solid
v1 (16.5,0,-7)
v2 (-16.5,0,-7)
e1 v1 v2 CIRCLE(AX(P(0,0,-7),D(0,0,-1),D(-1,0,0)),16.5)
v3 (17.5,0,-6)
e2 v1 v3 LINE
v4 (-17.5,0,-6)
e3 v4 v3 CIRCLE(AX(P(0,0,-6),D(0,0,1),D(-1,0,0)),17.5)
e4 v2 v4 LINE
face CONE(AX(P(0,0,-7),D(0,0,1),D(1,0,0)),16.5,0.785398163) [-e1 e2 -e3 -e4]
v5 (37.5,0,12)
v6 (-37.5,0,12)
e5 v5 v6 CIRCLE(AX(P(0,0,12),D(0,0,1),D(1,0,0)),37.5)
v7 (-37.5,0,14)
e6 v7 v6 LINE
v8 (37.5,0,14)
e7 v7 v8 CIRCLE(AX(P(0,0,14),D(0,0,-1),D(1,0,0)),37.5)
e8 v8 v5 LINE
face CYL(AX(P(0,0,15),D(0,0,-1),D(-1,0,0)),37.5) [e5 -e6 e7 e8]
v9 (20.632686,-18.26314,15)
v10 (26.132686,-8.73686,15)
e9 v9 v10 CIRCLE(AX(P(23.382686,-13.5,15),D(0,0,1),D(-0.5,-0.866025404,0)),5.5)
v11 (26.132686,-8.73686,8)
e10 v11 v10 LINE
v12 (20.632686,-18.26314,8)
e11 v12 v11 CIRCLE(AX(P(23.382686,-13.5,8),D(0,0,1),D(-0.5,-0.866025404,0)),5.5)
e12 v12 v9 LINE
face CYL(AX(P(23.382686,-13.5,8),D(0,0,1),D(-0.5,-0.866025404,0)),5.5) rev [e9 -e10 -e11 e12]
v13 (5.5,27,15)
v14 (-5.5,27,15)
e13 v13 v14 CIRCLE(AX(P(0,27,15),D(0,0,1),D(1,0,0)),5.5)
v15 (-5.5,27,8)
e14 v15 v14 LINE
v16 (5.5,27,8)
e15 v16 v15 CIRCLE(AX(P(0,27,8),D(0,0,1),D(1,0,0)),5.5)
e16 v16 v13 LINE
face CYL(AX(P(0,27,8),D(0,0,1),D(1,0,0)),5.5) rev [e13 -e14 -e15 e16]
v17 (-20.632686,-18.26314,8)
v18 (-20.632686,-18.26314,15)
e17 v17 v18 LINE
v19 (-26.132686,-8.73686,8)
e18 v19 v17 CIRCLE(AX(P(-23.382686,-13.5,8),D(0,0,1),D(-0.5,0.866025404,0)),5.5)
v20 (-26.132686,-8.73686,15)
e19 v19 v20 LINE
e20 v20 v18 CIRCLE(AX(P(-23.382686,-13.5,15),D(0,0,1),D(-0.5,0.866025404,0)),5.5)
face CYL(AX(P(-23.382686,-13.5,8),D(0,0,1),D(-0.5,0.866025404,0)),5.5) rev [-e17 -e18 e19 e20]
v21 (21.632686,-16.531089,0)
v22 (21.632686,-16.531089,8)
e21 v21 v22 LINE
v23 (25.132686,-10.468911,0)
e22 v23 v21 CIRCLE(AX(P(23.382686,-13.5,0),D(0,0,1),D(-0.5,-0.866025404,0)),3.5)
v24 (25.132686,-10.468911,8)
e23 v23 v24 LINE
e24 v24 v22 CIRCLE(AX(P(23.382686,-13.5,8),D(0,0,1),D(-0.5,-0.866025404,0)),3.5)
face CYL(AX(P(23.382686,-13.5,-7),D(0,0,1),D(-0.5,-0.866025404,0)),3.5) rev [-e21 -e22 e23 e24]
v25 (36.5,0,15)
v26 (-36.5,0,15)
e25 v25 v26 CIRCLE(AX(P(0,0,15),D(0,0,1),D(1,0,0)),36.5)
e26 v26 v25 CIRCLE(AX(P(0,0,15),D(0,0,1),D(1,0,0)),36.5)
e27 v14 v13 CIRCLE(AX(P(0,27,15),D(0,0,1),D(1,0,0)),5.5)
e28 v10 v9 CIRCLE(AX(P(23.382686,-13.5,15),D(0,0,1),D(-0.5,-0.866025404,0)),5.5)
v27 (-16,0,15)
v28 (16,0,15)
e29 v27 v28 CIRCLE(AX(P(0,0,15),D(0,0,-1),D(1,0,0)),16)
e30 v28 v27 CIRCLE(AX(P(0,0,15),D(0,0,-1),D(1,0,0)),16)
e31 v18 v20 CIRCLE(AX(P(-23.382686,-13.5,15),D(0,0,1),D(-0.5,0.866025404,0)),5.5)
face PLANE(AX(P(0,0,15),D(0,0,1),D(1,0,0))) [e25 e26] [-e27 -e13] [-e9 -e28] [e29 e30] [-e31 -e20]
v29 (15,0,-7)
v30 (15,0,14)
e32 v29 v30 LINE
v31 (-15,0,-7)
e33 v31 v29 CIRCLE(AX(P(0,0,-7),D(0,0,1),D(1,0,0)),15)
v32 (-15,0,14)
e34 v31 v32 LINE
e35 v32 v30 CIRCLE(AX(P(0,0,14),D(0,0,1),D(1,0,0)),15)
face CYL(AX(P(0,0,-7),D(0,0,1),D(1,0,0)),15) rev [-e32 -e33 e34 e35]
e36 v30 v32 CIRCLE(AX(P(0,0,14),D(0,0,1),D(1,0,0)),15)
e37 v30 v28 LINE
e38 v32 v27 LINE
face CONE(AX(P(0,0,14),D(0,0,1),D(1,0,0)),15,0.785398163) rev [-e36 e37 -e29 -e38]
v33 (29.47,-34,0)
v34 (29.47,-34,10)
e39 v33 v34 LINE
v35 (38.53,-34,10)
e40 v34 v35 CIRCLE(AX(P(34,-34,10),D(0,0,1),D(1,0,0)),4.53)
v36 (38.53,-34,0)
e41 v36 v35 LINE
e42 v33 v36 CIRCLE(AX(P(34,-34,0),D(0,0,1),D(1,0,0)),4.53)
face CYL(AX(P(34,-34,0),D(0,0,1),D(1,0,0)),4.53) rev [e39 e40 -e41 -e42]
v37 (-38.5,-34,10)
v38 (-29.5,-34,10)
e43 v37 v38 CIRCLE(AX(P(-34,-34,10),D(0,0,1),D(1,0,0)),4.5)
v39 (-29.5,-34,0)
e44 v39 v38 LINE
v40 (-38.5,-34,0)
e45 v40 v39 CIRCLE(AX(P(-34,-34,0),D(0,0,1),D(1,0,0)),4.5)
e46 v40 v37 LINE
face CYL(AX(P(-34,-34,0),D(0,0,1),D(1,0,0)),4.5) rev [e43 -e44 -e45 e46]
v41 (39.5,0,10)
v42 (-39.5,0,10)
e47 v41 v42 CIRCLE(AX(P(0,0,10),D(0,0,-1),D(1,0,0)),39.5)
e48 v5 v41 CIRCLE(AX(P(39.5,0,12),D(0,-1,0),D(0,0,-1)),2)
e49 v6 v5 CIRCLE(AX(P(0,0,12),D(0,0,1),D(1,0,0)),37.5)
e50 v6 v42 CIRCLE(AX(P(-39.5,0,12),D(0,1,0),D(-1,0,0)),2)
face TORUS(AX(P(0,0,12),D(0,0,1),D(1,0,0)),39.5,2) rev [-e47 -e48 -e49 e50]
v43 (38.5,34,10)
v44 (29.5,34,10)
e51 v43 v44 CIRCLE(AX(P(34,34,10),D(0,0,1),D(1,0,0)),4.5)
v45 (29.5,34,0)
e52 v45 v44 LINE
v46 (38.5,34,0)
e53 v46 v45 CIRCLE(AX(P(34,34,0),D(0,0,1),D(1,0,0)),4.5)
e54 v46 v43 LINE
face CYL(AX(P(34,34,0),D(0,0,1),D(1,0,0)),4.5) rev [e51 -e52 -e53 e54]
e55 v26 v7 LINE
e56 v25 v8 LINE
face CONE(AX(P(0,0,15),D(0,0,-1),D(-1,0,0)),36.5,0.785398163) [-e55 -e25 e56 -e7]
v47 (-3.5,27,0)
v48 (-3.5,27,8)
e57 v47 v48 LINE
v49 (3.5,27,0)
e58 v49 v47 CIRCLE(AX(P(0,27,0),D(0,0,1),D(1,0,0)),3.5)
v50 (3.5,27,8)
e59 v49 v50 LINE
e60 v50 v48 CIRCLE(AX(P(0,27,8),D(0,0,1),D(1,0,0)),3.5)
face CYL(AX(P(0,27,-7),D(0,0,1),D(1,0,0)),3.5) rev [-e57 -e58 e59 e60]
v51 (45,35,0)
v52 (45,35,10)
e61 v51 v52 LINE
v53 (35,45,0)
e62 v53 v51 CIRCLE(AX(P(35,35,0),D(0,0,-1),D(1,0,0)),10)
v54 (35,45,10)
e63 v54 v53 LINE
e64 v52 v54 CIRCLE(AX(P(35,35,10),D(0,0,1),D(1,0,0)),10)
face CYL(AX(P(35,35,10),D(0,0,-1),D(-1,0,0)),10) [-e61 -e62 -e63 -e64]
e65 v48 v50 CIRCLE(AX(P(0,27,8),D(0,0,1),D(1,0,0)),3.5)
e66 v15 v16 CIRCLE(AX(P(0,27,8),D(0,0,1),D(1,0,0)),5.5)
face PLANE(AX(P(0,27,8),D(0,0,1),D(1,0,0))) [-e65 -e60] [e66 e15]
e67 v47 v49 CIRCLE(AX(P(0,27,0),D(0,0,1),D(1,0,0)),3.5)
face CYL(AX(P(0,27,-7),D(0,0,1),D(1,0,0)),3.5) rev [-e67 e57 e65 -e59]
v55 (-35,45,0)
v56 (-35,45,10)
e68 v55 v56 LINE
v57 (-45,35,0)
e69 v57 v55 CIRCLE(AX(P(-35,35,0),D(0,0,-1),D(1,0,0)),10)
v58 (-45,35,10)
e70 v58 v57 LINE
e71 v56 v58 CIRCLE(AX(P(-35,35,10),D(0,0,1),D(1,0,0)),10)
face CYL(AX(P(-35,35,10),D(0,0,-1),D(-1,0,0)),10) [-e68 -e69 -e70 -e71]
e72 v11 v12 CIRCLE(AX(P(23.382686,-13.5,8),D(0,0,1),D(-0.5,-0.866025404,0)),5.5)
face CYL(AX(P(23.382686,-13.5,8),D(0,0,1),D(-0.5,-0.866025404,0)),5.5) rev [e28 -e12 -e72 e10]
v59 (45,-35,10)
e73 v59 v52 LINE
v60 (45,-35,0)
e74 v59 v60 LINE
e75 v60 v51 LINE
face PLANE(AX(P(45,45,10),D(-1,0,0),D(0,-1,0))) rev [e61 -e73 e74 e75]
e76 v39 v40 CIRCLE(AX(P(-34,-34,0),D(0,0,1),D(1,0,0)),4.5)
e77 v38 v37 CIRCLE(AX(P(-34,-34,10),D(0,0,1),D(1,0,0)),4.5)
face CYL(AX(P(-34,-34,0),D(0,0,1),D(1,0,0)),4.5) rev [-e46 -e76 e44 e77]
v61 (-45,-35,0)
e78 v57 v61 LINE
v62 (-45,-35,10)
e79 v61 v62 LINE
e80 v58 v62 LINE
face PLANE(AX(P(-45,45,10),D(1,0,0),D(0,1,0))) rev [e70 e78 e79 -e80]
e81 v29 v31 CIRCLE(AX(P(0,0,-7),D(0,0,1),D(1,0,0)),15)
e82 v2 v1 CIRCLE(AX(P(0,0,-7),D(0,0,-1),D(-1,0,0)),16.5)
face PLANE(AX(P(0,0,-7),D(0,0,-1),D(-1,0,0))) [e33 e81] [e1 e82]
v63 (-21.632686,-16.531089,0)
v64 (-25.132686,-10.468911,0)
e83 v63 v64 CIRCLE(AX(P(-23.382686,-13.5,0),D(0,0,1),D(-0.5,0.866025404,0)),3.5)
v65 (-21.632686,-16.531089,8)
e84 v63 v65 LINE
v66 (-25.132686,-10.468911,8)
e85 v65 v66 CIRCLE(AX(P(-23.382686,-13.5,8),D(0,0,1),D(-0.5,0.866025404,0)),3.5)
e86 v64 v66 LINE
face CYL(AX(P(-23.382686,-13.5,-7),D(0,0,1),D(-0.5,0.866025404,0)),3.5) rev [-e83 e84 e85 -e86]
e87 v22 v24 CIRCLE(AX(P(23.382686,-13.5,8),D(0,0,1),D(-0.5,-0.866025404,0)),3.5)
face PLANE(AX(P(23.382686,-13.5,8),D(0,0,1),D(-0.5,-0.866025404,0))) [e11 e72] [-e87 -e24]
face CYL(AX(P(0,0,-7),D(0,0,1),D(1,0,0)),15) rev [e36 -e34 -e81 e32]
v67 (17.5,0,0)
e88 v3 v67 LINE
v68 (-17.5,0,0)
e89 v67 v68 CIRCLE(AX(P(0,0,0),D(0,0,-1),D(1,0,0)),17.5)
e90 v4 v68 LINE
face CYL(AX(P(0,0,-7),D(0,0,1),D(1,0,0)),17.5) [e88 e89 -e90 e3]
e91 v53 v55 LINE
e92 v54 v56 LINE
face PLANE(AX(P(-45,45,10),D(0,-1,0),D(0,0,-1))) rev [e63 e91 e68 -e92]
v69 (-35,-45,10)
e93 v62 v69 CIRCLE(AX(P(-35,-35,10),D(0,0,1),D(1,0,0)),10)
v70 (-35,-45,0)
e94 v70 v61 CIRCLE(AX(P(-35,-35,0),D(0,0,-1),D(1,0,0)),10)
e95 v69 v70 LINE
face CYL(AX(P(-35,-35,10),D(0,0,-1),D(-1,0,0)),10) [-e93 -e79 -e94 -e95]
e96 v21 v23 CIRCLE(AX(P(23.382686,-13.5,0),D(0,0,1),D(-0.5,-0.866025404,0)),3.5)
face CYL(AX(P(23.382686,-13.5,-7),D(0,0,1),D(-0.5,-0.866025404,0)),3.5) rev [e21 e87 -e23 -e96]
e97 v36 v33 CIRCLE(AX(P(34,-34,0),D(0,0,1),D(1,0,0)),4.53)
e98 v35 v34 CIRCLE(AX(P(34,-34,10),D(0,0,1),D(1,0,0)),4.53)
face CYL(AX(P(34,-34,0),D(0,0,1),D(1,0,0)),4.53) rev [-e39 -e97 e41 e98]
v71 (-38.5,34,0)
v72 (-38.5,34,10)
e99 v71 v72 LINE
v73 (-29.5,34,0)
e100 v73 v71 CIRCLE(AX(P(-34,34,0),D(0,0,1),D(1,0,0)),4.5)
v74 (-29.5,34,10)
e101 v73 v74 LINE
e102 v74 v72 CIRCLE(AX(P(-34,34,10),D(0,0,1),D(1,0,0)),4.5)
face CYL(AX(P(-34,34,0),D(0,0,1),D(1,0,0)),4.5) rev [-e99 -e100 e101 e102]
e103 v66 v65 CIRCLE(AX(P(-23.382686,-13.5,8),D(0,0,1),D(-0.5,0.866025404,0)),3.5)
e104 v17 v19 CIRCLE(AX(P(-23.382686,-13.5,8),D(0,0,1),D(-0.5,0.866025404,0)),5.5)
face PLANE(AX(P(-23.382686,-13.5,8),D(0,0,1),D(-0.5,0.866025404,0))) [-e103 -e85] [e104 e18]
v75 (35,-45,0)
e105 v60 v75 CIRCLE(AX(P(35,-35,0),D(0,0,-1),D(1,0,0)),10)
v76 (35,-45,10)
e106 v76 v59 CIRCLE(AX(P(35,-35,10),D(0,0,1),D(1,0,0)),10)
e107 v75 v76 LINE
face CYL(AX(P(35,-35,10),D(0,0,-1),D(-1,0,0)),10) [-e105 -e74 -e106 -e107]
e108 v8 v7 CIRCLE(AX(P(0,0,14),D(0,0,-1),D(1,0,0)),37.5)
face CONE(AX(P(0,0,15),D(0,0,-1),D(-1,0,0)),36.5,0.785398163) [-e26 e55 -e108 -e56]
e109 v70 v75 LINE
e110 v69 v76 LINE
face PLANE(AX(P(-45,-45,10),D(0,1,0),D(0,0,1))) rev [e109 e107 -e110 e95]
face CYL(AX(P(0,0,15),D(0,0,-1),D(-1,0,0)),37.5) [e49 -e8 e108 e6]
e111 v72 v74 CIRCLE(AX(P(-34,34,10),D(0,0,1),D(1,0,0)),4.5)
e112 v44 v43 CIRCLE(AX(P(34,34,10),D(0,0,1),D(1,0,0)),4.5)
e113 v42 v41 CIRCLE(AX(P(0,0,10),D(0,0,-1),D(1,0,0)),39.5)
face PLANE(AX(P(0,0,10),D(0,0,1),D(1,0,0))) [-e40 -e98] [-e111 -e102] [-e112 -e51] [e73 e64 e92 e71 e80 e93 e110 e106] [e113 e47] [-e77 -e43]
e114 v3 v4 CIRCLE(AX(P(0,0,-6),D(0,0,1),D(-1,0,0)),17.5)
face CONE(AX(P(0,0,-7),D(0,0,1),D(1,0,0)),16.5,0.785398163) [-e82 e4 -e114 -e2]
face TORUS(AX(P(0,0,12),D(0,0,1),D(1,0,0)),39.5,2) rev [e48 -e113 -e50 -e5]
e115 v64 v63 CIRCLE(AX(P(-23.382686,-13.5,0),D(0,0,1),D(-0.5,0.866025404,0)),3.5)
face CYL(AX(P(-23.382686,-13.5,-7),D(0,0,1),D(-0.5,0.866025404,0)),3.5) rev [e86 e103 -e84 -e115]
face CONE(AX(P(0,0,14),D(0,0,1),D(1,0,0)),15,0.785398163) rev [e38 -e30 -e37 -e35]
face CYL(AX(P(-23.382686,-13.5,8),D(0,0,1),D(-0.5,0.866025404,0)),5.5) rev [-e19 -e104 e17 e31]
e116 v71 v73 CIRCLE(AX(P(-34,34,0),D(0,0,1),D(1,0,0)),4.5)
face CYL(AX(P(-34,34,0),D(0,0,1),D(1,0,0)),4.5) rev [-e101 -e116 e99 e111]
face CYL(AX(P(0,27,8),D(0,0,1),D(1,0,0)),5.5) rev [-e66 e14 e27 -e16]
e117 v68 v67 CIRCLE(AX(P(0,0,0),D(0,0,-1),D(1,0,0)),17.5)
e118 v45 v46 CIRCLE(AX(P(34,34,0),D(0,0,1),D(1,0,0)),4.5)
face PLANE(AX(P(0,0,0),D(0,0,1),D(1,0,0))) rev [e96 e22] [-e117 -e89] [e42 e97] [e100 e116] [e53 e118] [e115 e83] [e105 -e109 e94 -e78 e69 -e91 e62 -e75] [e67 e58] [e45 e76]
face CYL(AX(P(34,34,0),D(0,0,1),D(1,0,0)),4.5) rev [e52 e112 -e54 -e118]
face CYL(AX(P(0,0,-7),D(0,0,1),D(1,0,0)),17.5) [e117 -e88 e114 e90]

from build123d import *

# Parameters (mm, degrees)
SKETCH_1_W               = 90
SKETCH_1_H               = 90
EXTRUDE_1_DEPTH          = 10
FILLET_1_R               = 10
SKETCH_2_R               = 4.5
SKETCH_2_R_2             = 4.53
CUT_EXTRUDE_1_DEPTH      = 65.420493634
SKETCH_3_R               = 37.5
EXTRUDE_2_DEPTH          = 5
SKETCH_4_R               = 17.5
EXTRUDE_3_DEPTH          = 7
SKETCH_5_R               = 15
CUT_EXTRUDE_2_DEPTH      = 68.334983478
SKETCH_6_R               = 5.5
CUT_EXTRUDE_3_DEPTH      = 7
SKETCH_7_R               = 3.5
CUT_EXTRUDE_4_DEPTH      = 66.383484153
PATTERN_CIRCULAR_1_COUNT = 3
FILLET_2_R               = 2
CHAMFER_1_SIZE           = 1


with BuildPart() as part:
    # 草图1 → 凸台-拉伸1 (new body)
    with BuildSketch(Plane.XY):
        Rectangle(SKETCH_1_W, SKETCH_1_H)
    extrude(amount=EXTRUDE_1_DEPTH)

    # 圆角1
    fillet_1_edges = [part.edges().sort_by_distance(p)[0] for p in [
        (45, -45, 5),
        (-45, -45, 5),
        (-45, 45, 5),
        (45, 45, 5),
    ]]
    fillet(fillet_1_edges, radius=FILLET_1_R)

    # 草图2 → 切除-拉伸1 (cut, through all)
    with BuildSketch(Plane.XY.offset(10)):
        with Locations((-34, 34)):
            Circle(SKETCH_2_R)
        with Locations((34, 34)):
            Circle(SKETCH_2_R)
        with Locations((-34, -34)):
            Circle(SKETCH_2_R)
        with Locations((34, -34)):
            Circle(SKETCH_2_R_2)
    extrude(amount=-CUT_EXTRUDE_1_DEPTH, mode=Mode.SUBTRACT)

    # 草图3 → 凸台-拉伸2 (add)
    with BuildSketch(Plane.XY.offset(10)):
        Circle(SKETCH_3_R)
    extrude(amount=EXTRUDE_2_DEPTH)

    # 草图4 → 凸台-拉伸3 (add)
    with BuildSketch(Plane(origin=(0, 0, 0), x_dir=(-1, 0, 0), z_dir=(0, 0, -1))):
        with Locations(Location((0, 0, 0), (0, 0, 180))):
            Circle(SKETCH_4_R)
    extrude(amount=EXTRUDE_3_DEPTH)

    # 草图5 → 切除-拉伸2 (cut, through all)
    with BuildSketch(Plane.XY.offset(15)):
        Circle(SKETCH_5_R)
    extrude(amount=-CUT_EXTRUDE_2_DEPTH, mode=Mode.SUBTRACT)

    # 草图6 → 切除-拉伸3 (cut)
    with BuildSketch(Plane.XY.offset(15)):
        with Locations((0, 27)):
            Circle(SKETCH_6_R)
    cut_extrude_3 = extrude(amount=-CUT_EXTRUDE_3_DEPTH, mode=Mode.SUBTRACT)

    # 草图7 → 切除-拉伸4 (cut, through all)
    with BuildSketch(Plane.XY.offset(8)):
        with Locations((0, 27)):
            Circle(SKETCH_7_R)
    cut_extrude_4 = extrude(amount=-CUT_EXTRUDE_4_DEPTH, mode=Mode.SUBTRACT)

    # 阵列(圆周)1: 切除-拉伸3, 切除-拉伸4 ×3 about axis
    pattern_circular_1_axis = Axis((0, 0, 0), (0, 0, 1))
    add([cut_extrude_3.rotate(pattern_circular_1_axis, i * 360 / PATTERN_CIRCULAR_1_COUNT) for i in range(1, PATTERN_CIRCULAR_1_COUNT)], mode=Mode.SUBTRACT)
    add([cut_extrude_4.rotate(pattern_circular_1_axis, i * 360 / PATTERN_CIRCULAR_1_COUNT) for i in range(1, PATTERN_CIRCULAR_1_COUNT)], mode=Mode.SUBTRACT)

    # 圆角2
    fillet_2_edges = [part.edges().sort_by_distance(p)[0] for p in [
        (-37.5, 0, 10),
    ]]
    fillet(fillet_2_edges, radius=FILLET_2_R)

    # 倒角1
    chamfer_1_edges = [part.edges().sort_by_distance(p)[0] for p in [
        (-37.5, 0, 15),
        (-17.5, 0, -7),
        (-15, 0, 15),
    ]]
    chamfer(chamfer_1_edges, length=CHAMFER_1_SIZE)


solid = part.part
